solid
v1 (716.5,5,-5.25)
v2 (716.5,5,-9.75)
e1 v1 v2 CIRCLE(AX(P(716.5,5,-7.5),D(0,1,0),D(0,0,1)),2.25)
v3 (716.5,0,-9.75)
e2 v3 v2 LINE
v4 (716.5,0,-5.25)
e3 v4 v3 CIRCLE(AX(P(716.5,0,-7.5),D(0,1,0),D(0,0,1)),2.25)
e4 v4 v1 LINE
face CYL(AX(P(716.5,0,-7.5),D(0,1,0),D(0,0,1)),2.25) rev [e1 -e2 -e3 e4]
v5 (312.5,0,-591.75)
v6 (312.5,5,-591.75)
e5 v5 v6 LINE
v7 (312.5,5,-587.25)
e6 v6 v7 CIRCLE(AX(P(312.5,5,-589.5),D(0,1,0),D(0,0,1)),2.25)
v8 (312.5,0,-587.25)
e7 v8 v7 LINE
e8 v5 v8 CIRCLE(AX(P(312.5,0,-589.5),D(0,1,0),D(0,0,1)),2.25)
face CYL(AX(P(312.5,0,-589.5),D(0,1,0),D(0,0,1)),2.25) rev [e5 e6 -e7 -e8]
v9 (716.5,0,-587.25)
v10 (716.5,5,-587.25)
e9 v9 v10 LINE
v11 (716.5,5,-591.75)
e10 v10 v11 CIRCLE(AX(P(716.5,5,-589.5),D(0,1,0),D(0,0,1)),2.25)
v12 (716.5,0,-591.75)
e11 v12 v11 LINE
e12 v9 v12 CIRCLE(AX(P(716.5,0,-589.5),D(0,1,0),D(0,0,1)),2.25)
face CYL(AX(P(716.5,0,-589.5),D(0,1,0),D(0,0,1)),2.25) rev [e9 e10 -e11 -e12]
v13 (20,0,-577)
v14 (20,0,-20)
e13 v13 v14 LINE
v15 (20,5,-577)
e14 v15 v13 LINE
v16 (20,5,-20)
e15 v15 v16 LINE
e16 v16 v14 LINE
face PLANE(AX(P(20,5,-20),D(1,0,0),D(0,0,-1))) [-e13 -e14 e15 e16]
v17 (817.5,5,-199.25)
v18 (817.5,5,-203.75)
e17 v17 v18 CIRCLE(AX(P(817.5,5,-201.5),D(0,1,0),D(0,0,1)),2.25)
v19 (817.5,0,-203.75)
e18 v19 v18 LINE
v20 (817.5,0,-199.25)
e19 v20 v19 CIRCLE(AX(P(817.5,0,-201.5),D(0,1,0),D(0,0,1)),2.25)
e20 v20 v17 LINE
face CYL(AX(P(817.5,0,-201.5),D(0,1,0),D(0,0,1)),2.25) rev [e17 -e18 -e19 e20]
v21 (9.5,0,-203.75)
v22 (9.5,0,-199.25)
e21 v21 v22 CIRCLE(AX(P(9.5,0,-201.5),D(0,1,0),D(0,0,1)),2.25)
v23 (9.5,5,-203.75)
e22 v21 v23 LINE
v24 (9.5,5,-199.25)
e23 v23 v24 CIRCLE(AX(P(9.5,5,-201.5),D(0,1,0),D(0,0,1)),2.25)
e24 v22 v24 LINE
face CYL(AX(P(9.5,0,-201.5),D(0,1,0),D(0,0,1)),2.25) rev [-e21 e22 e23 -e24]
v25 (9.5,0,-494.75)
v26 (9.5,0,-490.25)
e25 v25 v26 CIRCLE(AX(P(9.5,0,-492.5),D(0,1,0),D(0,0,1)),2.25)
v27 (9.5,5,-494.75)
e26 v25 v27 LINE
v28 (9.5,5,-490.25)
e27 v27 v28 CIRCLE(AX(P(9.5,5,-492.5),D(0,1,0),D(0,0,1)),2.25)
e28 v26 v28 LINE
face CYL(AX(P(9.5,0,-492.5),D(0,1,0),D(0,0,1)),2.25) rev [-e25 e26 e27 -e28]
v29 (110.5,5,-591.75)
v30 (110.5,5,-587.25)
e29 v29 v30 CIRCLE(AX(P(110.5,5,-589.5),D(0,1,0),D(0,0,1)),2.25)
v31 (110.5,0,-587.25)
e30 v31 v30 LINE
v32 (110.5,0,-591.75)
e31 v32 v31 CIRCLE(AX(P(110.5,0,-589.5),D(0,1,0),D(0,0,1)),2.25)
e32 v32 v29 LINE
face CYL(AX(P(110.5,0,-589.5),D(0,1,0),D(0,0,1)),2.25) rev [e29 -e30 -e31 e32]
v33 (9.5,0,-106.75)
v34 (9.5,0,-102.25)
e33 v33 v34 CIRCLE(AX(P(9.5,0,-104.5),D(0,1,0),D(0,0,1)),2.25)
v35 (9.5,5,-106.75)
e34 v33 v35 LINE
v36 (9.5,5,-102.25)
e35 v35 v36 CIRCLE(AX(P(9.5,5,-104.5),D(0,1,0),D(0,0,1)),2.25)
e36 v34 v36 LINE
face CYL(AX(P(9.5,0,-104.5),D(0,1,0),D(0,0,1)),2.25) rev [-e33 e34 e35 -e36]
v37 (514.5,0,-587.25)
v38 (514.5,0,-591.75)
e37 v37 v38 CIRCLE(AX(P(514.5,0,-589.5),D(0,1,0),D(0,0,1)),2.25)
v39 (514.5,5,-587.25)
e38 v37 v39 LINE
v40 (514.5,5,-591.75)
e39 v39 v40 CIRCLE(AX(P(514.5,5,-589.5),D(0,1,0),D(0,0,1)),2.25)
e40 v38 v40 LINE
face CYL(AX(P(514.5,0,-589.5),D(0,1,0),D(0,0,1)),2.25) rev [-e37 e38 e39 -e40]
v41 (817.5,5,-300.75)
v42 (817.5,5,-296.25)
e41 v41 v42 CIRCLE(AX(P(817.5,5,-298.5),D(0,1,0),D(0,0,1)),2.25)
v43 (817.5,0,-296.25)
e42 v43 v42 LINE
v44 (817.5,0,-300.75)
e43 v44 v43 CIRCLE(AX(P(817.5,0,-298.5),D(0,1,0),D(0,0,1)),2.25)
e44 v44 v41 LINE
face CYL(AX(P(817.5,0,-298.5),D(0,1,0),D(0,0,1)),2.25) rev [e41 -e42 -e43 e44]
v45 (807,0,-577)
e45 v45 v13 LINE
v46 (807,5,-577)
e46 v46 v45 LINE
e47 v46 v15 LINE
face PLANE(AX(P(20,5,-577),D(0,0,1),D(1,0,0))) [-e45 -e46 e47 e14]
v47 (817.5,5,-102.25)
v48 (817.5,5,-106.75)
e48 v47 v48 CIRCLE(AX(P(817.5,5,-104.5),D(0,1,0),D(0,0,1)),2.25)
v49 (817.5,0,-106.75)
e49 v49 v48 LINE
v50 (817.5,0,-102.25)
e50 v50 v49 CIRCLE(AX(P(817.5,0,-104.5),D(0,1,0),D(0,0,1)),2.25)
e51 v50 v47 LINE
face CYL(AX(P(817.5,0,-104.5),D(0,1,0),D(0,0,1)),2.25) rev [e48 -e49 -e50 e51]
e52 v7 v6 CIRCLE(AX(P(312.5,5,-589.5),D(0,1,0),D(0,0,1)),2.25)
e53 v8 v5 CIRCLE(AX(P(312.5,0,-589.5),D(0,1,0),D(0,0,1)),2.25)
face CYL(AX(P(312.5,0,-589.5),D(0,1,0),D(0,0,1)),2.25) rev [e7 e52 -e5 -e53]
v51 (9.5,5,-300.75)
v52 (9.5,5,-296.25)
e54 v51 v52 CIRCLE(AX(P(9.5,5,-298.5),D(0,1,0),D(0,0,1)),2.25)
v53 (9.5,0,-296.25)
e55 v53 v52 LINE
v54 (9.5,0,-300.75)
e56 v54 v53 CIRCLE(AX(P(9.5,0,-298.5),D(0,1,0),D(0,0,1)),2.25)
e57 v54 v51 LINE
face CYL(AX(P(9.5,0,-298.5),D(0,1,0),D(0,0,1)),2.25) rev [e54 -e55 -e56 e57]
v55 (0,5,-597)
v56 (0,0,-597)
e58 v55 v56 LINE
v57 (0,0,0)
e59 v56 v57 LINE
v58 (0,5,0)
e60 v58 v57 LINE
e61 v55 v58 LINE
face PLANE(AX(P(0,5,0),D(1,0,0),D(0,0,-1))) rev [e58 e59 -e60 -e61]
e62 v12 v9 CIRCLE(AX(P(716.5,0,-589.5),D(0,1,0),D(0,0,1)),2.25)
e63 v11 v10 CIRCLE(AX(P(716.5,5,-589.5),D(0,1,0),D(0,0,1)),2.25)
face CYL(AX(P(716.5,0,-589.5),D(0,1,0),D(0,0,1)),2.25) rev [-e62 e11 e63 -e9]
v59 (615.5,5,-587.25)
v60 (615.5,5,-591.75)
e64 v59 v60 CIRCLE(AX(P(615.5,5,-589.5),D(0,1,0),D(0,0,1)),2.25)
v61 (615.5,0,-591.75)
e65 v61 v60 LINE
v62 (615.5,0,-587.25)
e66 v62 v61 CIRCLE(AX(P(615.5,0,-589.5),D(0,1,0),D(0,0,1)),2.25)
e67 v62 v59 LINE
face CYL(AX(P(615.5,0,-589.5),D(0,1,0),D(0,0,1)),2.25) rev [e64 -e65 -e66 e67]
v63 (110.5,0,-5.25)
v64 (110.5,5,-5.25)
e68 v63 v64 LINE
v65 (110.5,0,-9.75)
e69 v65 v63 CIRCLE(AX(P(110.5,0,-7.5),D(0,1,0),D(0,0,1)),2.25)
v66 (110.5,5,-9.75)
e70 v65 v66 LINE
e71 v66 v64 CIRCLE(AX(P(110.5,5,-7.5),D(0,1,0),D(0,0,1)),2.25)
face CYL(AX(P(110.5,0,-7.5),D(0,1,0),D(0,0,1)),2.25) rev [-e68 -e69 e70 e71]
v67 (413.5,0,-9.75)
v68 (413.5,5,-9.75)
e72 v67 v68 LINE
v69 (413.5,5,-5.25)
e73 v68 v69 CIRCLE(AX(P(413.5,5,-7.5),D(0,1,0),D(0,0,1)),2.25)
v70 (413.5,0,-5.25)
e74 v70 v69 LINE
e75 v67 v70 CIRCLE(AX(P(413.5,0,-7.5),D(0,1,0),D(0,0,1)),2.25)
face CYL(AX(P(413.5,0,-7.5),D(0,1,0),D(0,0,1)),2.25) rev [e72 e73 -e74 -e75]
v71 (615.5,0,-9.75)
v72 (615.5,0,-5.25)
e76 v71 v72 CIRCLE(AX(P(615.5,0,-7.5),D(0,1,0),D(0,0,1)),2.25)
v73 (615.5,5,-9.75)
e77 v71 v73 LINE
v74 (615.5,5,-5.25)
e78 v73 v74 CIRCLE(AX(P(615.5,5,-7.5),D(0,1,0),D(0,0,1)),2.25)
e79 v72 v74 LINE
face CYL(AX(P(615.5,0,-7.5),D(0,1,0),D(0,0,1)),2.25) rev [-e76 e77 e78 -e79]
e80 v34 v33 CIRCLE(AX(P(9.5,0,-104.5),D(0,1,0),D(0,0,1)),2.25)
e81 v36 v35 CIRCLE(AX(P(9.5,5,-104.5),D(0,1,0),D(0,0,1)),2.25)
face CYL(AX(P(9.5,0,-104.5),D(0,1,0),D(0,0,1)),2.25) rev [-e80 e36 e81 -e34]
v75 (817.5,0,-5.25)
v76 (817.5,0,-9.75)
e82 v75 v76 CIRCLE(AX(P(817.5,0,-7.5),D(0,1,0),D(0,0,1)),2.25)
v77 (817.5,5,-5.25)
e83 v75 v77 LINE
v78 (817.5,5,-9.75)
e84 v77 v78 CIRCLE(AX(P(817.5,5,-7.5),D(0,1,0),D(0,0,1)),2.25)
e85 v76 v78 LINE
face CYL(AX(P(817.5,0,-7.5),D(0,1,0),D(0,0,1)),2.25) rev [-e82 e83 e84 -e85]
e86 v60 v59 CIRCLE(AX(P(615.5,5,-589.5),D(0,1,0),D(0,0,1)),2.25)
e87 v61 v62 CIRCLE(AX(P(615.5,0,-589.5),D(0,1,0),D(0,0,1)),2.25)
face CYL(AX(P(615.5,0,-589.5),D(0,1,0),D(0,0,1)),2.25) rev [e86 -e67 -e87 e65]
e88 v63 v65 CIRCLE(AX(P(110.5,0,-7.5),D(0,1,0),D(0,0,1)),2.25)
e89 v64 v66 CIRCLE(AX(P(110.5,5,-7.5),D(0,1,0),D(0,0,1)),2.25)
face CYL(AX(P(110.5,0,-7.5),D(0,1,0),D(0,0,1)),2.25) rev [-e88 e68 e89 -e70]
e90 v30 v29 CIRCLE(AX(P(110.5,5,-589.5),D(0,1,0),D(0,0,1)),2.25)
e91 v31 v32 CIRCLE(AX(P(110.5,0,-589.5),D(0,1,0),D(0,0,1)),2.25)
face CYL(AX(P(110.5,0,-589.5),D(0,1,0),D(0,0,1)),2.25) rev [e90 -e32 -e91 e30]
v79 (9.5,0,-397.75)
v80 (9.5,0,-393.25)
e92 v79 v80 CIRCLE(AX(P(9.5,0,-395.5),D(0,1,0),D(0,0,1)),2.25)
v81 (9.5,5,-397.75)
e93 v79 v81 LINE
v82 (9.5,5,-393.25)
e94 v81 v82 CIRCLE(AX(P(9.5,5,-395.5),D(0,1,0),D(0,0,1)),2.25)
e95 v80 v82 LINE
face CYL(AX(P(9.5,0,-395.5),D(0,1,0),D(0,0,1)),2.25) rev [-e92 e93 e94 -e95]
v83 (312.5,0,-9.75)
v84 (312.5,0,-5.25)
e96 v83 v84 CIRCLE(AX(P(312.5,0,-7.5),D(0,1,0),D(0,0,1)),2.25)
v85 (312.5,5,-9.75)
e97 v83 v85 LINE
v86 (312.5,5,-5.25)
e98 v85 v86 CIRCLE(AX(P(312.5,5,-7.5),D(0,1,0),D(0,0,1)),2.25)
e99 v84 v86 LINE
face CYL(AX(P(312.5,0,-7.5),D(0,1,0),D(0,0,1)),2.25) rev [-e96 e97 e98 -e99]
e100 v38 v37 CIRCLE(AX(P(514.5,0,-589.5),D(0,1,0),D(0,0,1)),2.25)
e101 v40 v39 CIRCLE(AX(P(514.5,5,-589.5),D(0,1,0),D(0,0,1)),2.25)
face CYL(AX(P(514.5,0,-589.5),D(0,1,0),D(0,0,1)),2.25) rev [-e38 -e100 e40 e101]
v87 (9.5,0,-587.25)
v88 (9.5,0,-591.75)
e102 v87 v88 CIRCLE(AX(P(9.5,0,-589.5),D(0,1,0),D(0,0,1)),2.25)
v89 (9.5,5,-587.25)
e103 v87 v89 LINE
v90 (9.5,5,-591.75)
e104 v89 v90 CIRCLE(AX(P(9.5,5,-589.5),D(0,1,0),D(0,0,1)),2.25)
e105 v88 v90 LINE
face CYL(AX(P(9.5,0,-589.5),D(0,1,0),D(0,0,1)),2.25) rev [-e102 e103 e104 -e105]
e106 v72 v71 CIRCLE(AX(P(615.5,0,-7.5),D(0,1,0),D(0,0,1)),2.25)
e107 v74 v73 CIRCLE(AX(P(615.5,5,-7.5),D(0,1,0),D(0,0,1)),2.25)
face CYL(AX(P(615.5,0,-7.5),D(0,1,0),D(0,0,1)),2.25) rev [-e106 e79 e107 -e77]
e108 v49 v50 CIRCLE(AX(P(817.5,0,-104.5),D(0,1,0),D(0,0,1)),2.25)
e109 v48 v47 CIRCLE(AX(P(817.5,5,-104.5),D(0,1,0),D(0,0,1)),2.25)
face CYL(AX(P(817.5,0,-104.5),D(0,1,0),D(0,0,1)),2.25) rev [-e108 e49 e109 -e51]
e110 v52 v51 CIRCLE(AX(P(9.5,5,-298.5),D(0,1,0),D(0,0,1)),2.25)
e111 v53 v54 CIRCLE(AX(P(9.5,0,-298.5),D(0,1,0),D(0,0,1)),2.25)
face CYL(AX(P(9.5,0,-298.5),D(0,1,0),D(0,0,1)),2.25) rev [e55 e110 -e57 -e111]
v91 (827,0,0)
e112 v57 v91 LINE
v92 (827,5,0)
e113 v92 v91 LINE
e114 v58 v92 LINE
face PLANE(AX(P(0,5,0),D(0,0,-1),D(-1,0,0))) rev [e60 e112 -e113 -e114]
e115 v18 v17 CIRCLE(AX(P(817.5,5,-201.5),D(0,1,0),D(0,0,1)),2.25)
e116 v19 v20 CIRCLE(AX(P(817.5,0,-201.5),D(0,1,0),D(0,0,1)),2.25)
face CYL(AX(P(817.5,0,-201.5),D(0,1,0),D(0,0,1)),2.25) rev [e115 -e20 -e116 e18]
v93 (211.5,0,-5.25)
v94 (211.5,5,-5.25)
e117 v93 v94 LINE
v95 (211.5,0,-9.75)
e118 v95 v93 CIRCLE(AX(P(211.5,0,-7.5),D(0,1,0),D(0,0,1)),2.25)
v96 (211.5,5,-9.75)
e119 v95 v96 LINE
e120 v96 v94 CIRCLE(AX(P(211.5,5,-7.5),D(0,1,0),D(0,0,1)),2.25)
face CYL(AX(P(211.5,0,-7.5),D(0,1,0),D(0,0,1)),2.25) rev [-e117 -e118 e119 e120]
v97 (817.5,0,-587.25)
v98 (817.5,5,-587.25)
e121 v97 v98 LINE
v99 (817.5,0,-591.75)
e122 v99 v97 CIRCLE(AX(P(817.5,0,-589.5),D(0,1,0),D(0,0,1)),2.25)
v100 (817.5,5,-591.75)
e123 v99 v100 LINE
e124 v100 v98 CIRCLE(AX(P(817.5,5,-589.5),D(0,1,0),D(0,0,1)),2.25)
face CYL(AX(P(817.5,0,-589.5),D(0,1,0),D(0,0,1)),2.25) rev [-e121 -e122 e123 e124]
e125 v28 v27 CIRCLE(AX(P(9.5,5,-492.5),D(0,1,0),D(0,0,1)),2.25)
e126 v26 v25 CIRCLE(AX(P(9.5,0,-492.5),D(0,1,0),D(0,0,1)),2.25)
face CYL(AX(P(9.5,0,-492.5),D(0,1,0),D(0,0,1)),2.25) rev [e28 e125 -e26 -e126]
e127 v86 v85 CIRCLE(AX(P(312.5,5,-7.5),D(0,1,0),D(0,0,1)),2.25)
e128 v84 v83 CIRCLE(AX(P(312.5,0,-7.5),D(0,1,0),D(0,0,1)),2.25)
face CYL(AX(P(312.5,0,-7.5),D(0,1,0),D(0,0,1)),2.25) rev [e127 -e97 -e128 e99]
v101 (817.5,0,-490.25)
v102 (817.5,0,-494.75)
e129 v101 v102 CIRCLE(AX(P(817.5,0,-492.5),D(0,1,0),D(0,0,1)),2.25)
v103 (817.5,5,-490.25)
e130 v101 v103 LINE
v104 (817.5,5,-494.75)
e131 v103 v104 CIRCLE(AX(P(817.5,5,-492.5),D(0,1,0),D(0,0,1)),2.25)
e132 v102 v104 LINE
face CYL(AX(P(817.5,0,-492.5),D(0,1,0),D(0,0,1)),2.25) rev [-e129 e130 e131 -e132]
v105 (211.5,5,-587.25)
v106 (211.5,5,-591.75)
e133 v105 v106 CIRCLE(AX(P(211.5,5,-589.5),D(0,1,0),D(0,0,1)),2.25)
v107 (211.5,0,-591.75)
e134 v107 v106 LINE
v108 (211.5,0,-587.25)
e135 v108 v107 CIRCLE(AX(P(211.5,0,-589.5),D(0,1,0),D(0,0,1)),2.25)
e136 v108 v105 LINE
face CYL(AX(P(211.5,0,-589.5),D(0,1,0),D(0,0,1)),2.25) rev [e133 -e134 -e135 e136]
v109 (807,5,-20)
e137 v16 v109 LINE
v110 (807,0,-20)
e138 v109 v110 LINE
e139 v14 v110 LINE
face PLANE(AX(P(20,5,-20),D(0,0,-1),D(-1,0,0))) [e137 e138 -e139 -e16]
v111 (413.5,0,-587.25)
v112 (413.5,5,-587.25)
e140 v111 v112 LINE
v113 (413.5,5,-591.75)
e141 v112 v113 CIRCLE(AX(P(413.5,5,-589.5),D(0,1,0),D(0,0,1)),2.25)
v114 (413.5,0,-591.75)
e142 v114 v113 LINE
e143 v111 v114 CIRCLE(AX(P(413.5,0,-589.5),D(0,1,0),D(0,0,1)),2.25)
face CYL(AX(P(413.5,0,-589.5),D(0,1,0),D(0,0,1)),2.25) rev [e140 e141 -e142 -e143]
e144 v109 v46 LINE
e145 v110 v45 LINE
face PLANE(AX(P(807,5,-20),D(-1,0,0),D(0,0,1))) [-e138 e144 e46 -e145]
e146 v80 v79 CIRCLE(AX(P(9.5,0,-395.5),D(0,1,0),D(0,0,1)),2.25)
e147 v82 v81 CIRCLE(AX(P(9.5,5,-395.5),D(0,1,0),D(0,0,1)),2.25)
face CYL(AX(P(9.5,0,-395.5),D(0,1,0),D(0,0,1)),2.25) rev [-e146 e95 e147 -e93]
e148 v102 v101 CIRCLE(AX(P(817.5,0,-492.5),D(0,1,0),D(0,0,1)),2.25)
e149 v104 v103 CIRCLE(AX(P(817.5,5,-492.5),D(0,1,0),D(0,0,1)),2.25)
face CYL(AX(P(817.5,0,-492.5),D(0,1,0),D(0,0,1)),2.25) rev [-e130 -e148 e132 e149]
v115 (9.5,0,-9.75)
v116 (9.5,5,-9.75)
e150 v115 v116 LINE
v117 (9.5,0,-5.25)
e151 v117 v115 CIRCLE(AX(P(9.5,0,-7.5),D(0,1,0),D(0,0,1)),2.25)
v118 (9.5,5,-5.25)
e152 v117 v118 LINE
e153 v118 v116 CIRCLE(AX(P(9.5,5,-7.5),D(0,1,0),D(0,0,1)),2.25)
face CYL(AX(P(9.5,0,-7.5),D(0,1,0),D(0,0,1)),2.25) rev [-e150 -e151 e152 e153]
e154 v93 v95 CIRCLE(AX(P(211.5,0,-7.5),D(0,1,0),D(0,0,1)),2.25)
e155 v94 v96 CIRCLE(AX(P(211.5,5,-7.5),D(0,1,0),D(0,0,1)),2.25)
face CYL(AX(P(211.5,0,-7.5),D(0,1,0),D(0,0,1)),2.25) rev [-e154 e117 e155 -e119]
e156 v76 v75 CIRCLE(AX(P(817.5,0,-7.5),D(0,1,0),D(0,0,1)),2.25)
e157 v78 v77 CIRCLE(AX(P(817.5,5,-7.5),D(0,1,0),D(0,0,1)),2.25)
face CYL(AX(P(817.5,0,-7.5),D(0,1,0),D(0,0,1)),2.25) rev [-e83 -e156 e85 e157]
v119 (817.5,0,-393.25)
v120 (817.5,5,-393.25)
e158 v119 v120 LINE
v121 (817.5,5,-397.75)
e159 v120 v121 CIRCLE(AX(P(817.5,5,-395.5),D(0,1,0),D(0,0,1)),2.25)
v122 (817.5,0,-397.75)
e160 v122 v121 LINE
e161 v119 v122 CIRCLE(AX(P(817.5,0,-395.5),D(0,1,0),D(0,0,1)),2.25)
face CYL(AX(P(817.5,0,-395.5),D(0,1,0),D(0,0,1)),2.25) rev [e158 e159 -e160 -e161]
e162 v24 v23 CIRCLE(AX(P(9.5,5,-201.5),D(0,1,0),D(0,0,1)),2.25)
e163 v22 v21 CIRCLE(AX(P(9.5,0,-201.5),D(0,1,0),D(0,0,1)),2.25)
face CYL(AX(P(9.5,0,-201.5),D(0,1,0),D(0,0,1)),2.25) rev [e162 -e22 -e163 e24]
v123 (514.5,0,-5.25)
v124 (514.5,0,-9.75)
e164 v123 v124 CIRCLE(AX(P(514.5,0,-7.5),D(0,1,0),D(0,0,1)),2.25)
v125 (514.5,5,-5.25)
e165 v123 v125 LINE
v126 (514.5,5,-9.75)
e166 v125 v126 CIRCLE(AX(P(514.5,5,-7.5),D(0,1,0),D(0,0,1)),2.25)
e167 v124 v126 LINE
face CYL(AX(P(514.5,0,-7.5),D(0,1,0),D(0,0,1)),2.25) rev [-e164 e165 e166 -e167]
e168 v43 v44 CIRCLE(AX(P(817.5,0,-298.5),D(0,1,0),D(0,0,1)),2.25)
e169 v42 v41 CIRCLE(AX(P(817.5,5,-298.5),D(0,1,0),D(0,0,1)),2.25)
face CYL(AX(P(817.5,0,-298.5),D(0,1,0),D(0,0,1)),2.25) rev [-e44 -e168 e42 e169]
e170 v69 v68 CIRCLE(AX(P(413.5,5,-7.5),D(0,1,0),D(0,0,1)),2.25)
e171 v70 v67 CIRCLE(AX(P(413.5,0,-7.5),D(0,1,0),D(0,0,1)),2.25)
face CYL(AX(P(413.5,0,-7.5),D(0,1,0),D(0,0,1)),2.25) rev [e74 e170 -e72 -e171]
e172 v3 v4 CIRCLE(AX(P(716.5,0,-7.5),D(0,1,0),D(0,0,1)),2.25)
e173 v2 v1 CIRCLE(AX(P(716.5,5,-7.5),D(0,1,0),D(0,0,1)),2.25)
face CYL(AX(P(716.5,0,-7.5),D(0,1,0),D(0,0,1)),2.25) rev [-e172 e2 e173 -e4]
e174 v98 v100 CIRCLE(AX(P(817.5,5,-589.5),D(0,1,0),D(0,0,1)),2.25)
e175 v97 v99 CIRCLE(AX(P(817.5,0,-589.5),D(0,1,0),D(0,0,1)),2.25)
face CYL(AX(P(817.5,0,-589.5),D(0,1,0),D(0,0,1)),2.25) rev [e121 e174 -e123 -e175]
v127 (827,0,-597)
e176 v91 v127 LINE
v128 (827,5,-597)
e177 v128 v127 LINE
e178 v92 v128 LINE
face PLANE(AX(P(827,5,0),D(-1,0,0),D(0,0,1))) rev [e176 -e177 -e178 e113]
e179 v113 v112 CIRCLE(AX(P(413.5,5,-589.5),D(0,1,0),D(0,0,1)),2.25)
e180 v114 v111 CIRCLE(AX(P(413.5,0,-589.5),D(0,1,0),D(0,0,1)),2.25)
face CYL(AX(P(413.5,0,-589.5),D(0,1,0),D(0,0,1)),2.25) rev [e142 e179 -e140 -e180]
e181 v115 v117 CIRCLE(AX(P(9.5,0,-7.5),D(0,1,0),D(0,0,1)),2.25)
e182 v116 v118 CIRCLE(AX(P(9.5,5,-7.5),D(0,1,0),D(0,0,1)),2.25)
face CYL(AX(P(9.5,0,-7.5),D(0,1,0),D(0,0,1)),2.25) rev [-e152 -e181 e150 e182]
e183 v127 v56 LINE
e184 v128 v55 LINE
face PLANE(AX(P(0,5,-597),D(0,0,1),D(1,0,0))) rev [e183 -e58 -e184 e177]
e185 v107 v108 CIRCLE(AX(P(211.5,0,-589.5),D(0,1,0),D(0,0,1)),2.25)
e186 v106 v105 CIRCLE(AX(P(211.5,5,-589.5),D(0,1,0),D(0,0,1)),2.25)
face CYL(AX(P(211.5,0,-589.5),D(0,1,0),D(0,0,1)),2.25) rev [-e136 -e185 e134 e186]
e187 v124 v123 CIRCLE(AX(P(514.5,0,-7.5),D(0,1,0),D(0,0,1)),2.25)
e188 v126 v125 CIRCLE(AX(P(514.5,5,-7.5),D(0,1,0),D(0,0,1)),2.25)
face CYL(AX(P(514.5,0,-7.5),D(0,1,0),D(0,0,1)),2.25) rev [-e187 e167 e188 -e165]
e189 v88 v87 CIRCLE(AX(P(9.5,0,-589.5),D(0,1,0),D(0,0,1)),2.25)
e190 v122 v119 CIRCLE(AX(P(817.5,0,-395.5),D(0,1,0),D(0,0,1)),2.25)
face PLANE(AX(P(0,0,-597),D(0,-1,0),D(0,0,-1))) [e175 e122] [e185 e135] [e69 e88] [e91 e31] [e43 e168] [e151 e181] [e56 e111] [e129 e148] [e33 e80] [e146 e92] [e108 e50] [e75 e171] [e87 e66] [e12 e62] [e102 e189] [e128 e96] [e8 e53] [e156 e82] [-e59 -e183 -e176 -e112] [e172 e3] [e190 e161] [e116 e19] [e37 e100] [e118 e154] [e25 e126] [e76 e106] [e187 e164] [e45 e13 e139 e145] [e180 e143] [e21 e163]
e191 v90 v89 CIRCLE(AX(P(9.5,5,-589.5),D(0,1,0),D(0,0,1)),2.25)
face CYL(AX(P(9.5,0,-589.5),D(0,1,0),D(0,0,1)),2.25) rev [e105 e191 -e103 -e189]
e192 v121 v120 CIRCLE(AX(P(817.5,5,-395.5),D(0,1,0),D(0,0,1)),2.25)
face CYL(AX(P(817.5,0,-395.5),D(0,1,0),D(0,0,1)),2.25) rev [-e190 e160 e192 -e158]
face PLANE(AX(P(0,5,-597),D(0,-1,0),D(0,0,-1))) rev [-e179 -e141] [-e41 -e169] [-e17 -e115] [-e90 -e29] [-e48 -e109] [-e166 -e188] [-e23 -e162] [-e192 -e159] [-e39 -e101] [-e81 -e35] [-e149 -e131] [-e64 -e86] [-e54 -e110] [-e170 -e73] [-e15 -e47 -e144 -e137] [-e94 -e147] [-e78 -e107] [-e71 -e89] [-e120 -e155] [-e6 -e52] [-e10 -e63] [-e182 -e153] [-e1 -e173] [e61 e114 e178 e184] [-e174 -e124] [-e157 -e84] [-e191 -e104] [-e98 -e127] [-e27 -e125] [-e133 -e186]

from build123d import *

# Parameters (mm, degrees)
SKETCH_1_W                        = 827
SKETCH_1_H                        = 597
SKETCH_1_W_2                      = 787
SKETCH_1_H_2                      = 557
EXTRUDE_1_DEPTH                   = 5
SKETCH_2_R                        = 2.25
CUT_EXTRUDE_1_DEPTH               = 5
PATTERN_LINEAR_1_COUNT            = 9
PATTERN_LINEAR_1_PITCH            = 101
PATTERN_LINEAR_2_COUNT            = 7
PATTERN_LINEAR_2_PITCH            = 97
PATTERN_LINEAR_3_COPY_1_SKETCH_R  = 2.25
PATTERN_LINEAR_3_COPY_1_DEPTH     = 5
PATTERN_LINEAR_3_COPY_2_SKETCH_R  = 2.25
PATTERN_LINEAR_3_COPY_2_DEPTH     = 5
PATTERN_LINEAR_3_COPY_3_SKETCH_R  = 2.25
PATTERN_LINEAR_3_COPY_3_DEPTH     = 5
PATTERN_LINEAR_3_COPY_4_SKETCH_R  = 2.25
PATTERN_LINEAR_3_COPY_4_DEPTH     = 5
PATTERN_LINEAR_3_COPY_5_SKETCH_R  = 2.25
PATTERN_LINEAR_3_COPY_5_DEPTH     = 5
PATTERN_LINEAR_3_COPY_6_SKETCH_R  = 2.25
PATTERN_LINEAR_3_COPY_6_DEPTH     = 5
PATTERN_LINEAR_3_COPY_7_SKETCH_R  = 2.25
PATTERN_LINEAR_3_COPY_7_DEPTH     = 5
PATTERN_LINEAR_3_COPY_8_SKETCH_R  = 2.25
PATTERN_LINEAR_3_COPY_8_DEPTH     = 5
PATTERN_LINEAR_3_COPY_9_SKETCH_R  = 2.25
PATTERN_LINEAR_3_COPY_9_DEPTH     = 5
PATTERN_LINEAR_3_COPY_10_SKETCH_R = 2.25
PATTERN_LINEAR_3_COPY_10_DEPTH    = 5
PATTERN_LINEAR_3_COPY_11_SKETCH_R = 2.25
PATTERN_LINEAR_3_COPY_11_DEPTH    = 5
PATTERN_LINEAR_3_COPY_12_SKETCH_R = 2.25
PATTERN_LINEAR_3_COPY_12_DEPTH    = 5
PATTERN_LINEAR_3_COPY_13_SKETCH_R = 2.25
PATTERN_LINEAR_3_COPY_13_DEPTH    = 5
PATTERN_LINEAR_3_COPY_14_SKETCH_R = 2.25
PATTERN_LINEAR_3_COPY_14_DEPTH    = 5
PATTERN_LINEAR_3_COPY_15_SKETCH_R = 2.25
PATTERN_LINEAR_3_COPY_15_DEPTH    = 5
PATTERN_LINEAR_3_COPY_16_SKETCH_R = 2.25
PATTERN_LINEAR_3_COPY_16_DEPTH    = 5
PATTERN_LINEAR_3_COPY_17_SKETCH_R = 2.25
PATTERN_LINEAR_3_COPY_17_DEPTH    = 5
PATTERN_LINEAR_3_COPY_18_SKETCH_R = 2.25
PATTERN_LINEAR_3_COPY_18_DEPTH    = 5
PATTERN_LINEAR_3_COPY_19_SKETCH_R = 2.25
PATTERN_LINEAR_3_COPY_19_DEPTH    = 5
PATTERN_LINEAR_3_COPY_20_SKETCH_R = 2.25
PATTERN_LINEAR_3_COPY_20_DEPTH    = 5
PATTERN_LINEAR_3_COPY_21_SKETCH_R = 2.25
PATTERN_LINEAR_3_COPY_21_DEPTH    = 5
PATTERN_LINEAR_3_COPY_22_SKETCH_R = 2.25
PATTERN_LINEAR_3_COPY_22_DEPTH    = 5
PATTERN_LINEAR_3_COPY_23_SKETCH_R = 2.25
PATTERN_LINEAR_3_COPY_23_DEPTH    = 5
PATTERN_LINEAR_3_COPY_24_SKETCH_R = 2.25
PATTERN_LINEAR_3_COPY_24_DEPTH    = 5
PATTERN_LINEAR_3_COPY_25_SKETCH_R = 2.25
PATTERN_LINEAR_3_COPY_25_DEPTH    = 5
PATTERN_LINEAR_3_COPY_26_SKETCH_R = 2.25
PATTERN_LINEAR_3_COPY_26_DEPTH    = 5
PATTERN_LINEAR_3_COPY_27_SKETCH_R = 2.25
PATTERN_LINEAR_3_COPY_27_DEPTH    = 5
PATTERN_LINEAR_3_COPY_28_SKETCH_R = 2.25
PATTERN_LINEAR_3_COPY_28_DEPTH    = 5
PATTERN_LINEAR_3_COPY_29_SKETCH_R = 2.25
PATTERN_LINEAR_3_COPY_29_DEPTH    = 5
PATTERN_LINEAR_3_COPY_30_SKETCH_R = 2.25
PATTERN_LINEAR_3_COPY_30_DEPTH    = 5
PATTERN_LINEAR_3_COPY_31_SKETCH_R = 2.25
PATTERN_LINEAR_3_COPY_31_DEPTH    = 5
PATTERN_LINEAR_3_COPY_32_SKETCH_R = 2.25
PATTERN_LINEAR_3_COPY_32_DEPTH    = 5
PATTERN_LINEAR_3_COPY_33_SKETCH_R = 2.25
PATTERN_LINEAR_3_COPY_33_DEPTH    = 5
PATTERN_LINEAR_3_COPY_34_SKETCH_R = 2.25
PATTERN_LINEAR_3_COPY_34_DEPTH    = 5
PATTERN_LINEAR_3_COPY_35_SKETCH_R = 2.25
PATTERN_LINEAR_3_COPY_35_DEPTH    = 5
PATTERN_LINEAR_3_COPY_36_SKETCH_R = 2.25
PATTERN_LINEAR_3_COPY_36_DEPTH    = 5
PATTERN_LINEAR_3_COPY_37_SKETCH_R = 2.25
PATTERN_LINEAR_3_COPY_37_DEPTH    = 5
PATTERN_LINEAR_3_COPY_38_SKETCH_R = 2.25
PATTERN_LINEAR_3_COPY_38_DEPTH    = 5
PATTERN_LINEAR_3_COPY_39_SKETCH_R = 2.25
PATTERN_LINEAR_3_COPY_39_DEPTH    = 5
PATTERN_LINEAR_3_COPY_40_SKETCH_R = 2.25
PATTERN_LINEAR_3_COPY_40_DEPTH    = 5
PATTERN_LINEAR_3_COPY_41_SKETCH_R = 2.25
PATTERN_LINEAR_3_COPY_41_DEPTH    = 5
PATTERN_LINEAR_3_COPY_42_SKETCH_R = 2.25
PATTERN_LINEAR_3_COPY_42_DEPTH    = 5
PATTERN_LINEAR_3_COPY_43_SKETCH_R = 2.25
PATTERN_LINEAR_3_COPY_43_DEPTH    = 5
PATTERN_LINEAR_3_COPY_44_SKETCH_R = 2.25
PATTERN_LINEAR_3_COPY_44_DEPTH    = 5
PATTERN_LINEAR_3_COPY_45_SKETCH_R = 2.25
PATTERN_LINEAR_3_COPY_45_DEPTH    = 5
PATTERN_LINEAR_3_COPY_46_SKETCH_R = 2.25
PATTERN_LINEAR_3_COPY_46_DEPTH    = 5
PATTERN_LINEAR_3_COPY_47_SKETCH_R = 2.25
PATTERN_LINEAR_3_COPY_47_DEPTH    = 5
PATTERN_LINEAR_3_COPY_48_SKETCH_R = 2.25
PATTERN_LINEAR_3_COPY_48_DEPTH    = 5
PATTERN_LINEAR_3_COPY_49_SKETCH_R = 2.25
PATTERN_LINEAR_3_COPY_49_DEPTH    = 5
PATTERN_LINEAR_3_COPY_50_SKETCH_R = 2.25
PATTERN_LINEAR_3_COPY_50_DEPTH    = 5
PATTERN_LINEAR_3_COPY_51_SKETCH_R = 2.25
PATTERN_LINEAR_3_COPY_51_DEPTH    = 5
PATTERN_LINEAR_3_COPY_52_SKETCH_R = 2.25
PATTERN_LINEAR_3_COPY_52_DEPTH    = 5
PATTERN_LINEAR_3_COPY_53_SKETCH_R = 2.25
PATTERN_LINEAR_3_COPY_53_DEPTH    = 5
PATTERN_LINEAR_3_COPY_54_SKETCH_R = 2.25
PATTERN_LINEAR_3_COPY_54_DEPTH    = 5
PATTERN_LINEAR_3_COPY_55_SKETCH_R = 2.25
PATTERN_LINEAR_3_COPY_55_DEPTH    = 5
PATTERN_LINEAR_3_COPY_56_SKETCH_R = 2.25
PATTERN_LINEAR_3_COPY_56_DEPTH    = 5


with BuildPart() as part:
    # 草图1 → 拉伸1 (new body)
    with BuildSketch(Plane(origin=(0, 0, 0), x_dir=(1, 0, 0), z_dir=(0, 1, 0))):
        with Locations((413.5, 298.5)):
            Rectangle(SKETCH_1_W, SKETCH_1_H)
        with Locations((413.5, 298.5)):
            Rectangle(SKETCH_1_W_2, SKETCH_1_H_2, mode=Mode.SUBTRACT)
    extrude(amount=EXTRUDE_1_DEPTH)

    # 草图2 → 切除-拉伸1 (cut)
    with BuildSketch(Plane(origin=(0, 5, 0), x_dir=(-1, 0, 0), z_dir=(0, 1, 0))):
        with Locations(Location((-817.5, -589.5, 0), (0, 0, 90))):
            Circle(SKETCH_2_R)
    cut_extrude_1 = extrude(amount=-CUT_EXTRUDE_1_DEPTH, mode=Mode.SUBTRACT)

    # 阵列(线性)1: 切除-拉伸1 ×9
    with Locations(*[(-i * PATTERN_LINEAR_1_PITCH, 0, 0) for i in range(1, PATTERN_LINEAR_1_COUNT)]):
        add(cut_extrude_1, mode=Mode.SUBTRACT)

    # 阵列(线性)2: 切除-拉伸1 ×7
    with Locations(*[(0, 0, i * PATTERN_LINEAR_2_PITCH) for i in range(1, PATTERN_LINEAR_2_COUNT)]):
        add(cut_extrude_1, mode=Mode.SUBTRACT)

    # 阵列(线性)3 copy 1 sketch → 阵列(线性)3 copy 1 (cut)
    with BuildSketch(Plane(origin=(-101, 5, 97), x_dir=(-1, 0, 0), z_dir=(0, 1, 0))):
        with Locations(Location((-817.5, -589.5, 0), (0, 0, 90))):
            Circle(PATTERN_LINEAR_3_COPY_1_SKETCH_R)
    extrude(amount=-PATTERN_LINEAR_3_COPY_1_DEPTH, mode=Mode.SUBTRACT)

    # 阵列(线性)3 copy 2 sketch → 阵列(线性)3 copy 2 (cut)
    with BuildSketch(Plane(origin=(-202, 5, 97), x_dir=(-1, 0, 0), z_dir=(0, 1, 0))):
        with Locations(Location((-817.5, -589.5, 0), (0, 0, 90))):
            Circle(PATTERN_LINEAR_3_COPY_2_SKETCH_R)
    extrude(amount=-PATTERN_LINEAR_3_COPY_2_DEPTH, mode=Mode.SUBTRACT)

    # 阵列(线性)3 copy 3 sketch → 阵列(线性)3 copy 3 (cut)
    with BuildSketch(Plane(origin=(-303, 5, 97), x_dir=(-1, 0, 0), z_dir=(0, 1, 0))):
        with Locations(Location((-817.5, -589.5, 0), (0, 0, 90))):
            Circle(PATTERN_LINEAR_3_COPY_3_SKETCH_R)
    extrude(amount=-PATTERN_LINEAR_3_COPY_3_DEPTH, mode=Mode.SUBTRACT)

    # 阵列(线性)3 copy 4 sketch → 阵列(线性)3 copy 4 (cut)
    with BuildSketch(Plane(origin=(-404, 5, 97), x_dir=(-1, 0, 0), z_dir=(0, 1, 0))):
        with Locations(Location((-817.5, -589.5, 0), (0, 0, 90))):
            Circle(PATTERN_LINEAR_3_COPY_4_SKETCH_R)
    extrude(amount=-PATTERN_LINEAR_3_COPY_4_DEPTH, mode=Mode.SUBTRACT)

    # 阵列(线性)3 copy 5 sketch → 阵列(线性)3 copy 5 (cut)
    with BuildSketch(Plane(origin=(-505, 5, 97), x_dir=(-1, 0, 0), z_dir=(0, 1, 0))):
        with Locations(Location((-817.5, -589.5, 0), (0, 0, 90))):
            Circle(PATTERN_LINEAR_3_COPY_5_SKETCH_R)
    extrude(amount=-PATTERN_LINEAR_3_COPY_5_DEPTH, mode=Mode.SUBTRACT)

    # 阵列(线性)3 copy 6 sketch → 阵列(线性)3 copy 6 (cut)
    with BuildSketch(Plane(origin=(-606, 5, 97), x_dir=(-1, 0, 0), z_dir=(0, 1, 0))):
        with Locations(Location((-817.5, -589.5, 0), (0, 0, 90))):
            Circle(PATTERN_LINEAR_3_COPY_6_SKETCH_R)
    extrude(amount=-PATTERN_LINEAR_3_COPY_6_DEPTH, mode=Mode.SUBTRACT)

    # 阵列(线性)3 copy 7 sketch → 阵列(线性)3 copy 7 (cut)
    with BuildSketch(Plane(origin=(-707, 5, 97), x_dir=(-1, 0, 0), z_dir=(0, 1, 0))):
        with Locations(Location((-817.5, -589.5, 0), (0, 0, 90))):
            Circle(PATTERN_LINEAR_3_COPY_7_SKETCH_R)
    extrude(amount=-PATTERN_LINEAR_3_COPY_7_DEPTH, mode=Mode.SUBTRACT)

    # 阵列(线性)3 copy 8 sketch → 阵列(线性)3 copy 8 (cut)
    with BuildSketch(Plane(origin=(-808, 5, 97), x_dir=(-1, 0, 0), z_dir=(0, 1, 0))):
        with Locations(Location((-817.5, -589.5, 0), (0, 0, 90))):
            Circle(PATTERN_LINEAR_3_COPY_8_SKETCH_R)
    extrude(amount=-PATTERN_LINEAR_3_COPY_8_DEPTH, mode=Mode.SUBTRACT)

    # 阵列(线性)3 copy 9 sketch → 阵列(线性)3 copy 9 (cut)
    with BuildSketch(Plane(origin=(-101, 5, 194), x_dir=(-1, 0, 0), z_dir=(0, 1, 0))):
        with Locations(Location((-817.5, -589.5, 0), (0, 0, 90))):
            Circle(PATTERN_LINEAR_3_COPY_9_SKETCH_R)
    extrude(amount=-PATTERN_LINEAR_3_COPY_9_DEPTH, mode=Mode.SUBTRACT)

    # 阵列(线性)3 copy 10 sketch → 阵列(线性)3 copy 10 (cut)
    with BuildSketch(Plane(origin=(-202, 5, 194), x_dir=(-1, 0, 0), z_dir=(0, 1, 0))):
        with Locations(Location((-817.5, -589.5, 0), (0, 0, 90))):
            Circle(PATTERN_LINEAR_3_COPY_10_SKETCH_R)
    extrude(amount=-PATTERN_LINEAR_3_COPY_10_DEPTH, mode=Mode.SUBTRACT)

    # 阵列(线性)3 copy 11 sketch → 阵列(线性)3 copy 11 (cut)
    with BuildSketch(Plane(origin=(-303, 5, 194), x_dir=(-1, 0, 0), z_dir=(0, 1, 0))):
        with Locations(Location((-817.5, -589.5, 0), (0, 0, 90))):
            Circle(PATTERN_LINEAR_3_COPY_11_SKETCH_R)
    extrude(amount=-PATTERN_LINEAR_3_COPY_11_DEPTH, mode=Mode.SUBTRACT)

    # 阵列(线性)3 copy 12 sketch → 阵列(线性)3 copy 12 (cut)
    with BuildSketch(Plane(origin=(-404, 5, 194), x_dir=(-1, 0, 0), z_dir=(0, 1, 0))):
        with Locations(Location((-817.5, -589.5, 0), (0, 0, 90))):
            Circle(PATTERN_LINEAR_3_COPY_12_SKETCH_R)
    extrude(amount=-PATTERN_LINEAR_3_COPY_12_DEPTH, mode=Mode.SUBTRACT)

    # 阵列(线性)3 copy 13 sketch → 阵列(线性)3 copy 13 (cut)
    with BuildSketch(Plane(origin=(-505, 5, 194), x_dir=(-1, 0, 0), z_dir=(0, 1, 0))):
        with Locations(Location((-817.5, -589.5, 0), (0, 0, 90))):
            Circle(PATTERN_LINEAR_3_COPY_13_SKETCH_R)
    extrude(amount=-PATTERN_LINEAR_3_COPY_13_DEPTH, mode=Mode.SUBTRACT)

    # 阵列(线性)3 copy 14 sketch → 阵列(线性)3 copy 14 (cut)
    with BuildSketch(Plane(origin=(-606, 5, 194), x_dir=(-1, 0, 0), z_dir=(0, 1, 0))):
        with Locations(Location((-817.5, -589.5, 0), (0, 0, 90))):
            Circle(PATTERN_LINEAR_3_COPY_14_SKETCH_R)
    extrude(amount=-PATTERN_LINEAR_3_COPY_14_DEPTH, mode=Mode.SUBTRACT)

    # 阵列(线性)3 copy 15 sketch → 阵列(线性)3 copy 15 (cut)
    with BuildSketch(Plane(origin=(-707, 5, 194), x_dir=(-1, 0, 0), z_dir=(0, 1, 0))):
        with Locations(Location((-817.5, -589.5, 0), (0, 0, 90))):
            Circle(PATTERN_LINEAR_3_COPY_15_SKETCH_R)
    extrude(amount=-PATTERN_LINEAR_3_COPY_15_DEPTH, mode=Mode.SUBTRACT)

    # 阵列(线性)3 copy 16 sketch → 阵列(线性)3 copy 16 (cut)
    with BuildSketch(Plane(origin=(-808, 5, 194), x_dir=(-1, 0, 0), z_dir=(0, 1, 0))):
        with Locations(Location((-817.5, -589.5, 0), (0, 0, 90))):
            Circle(PATTERN_LINEAR_3_COPY_16_SKETCH_R)
    extrude(amount=-PATTERN_LINEAR_3_COPY_16_DEPTH, mode=Mode.SUBTRACT)

    # 阵列(线性)3 copy 17 sketch → 阵列(线性)3 copy 17 (cut)
    with BuildSketch(Plane(origin=(-101, 5, 291), x_dir=(-1, 0, 0), z_dir=(0, 1, 0))):
        with Locations(Location((-817.5, -589.5, 0), (0, 0, 90))):
            Circle(PATTERN_LINEAR_3_COPY_17_SKETCH_R)
    extrude(amount=-PATTERN_LINEAR_3_COPY_17_DEPTH, mode=Mode.SUBTRACT)

    # 阵列(线性)3 copy 18 sketch → 阵列(线性)3 copy 18 (cut)
    with BuildSketch(Plane(origin=(-202, 5, 291), x_dir=(-1, 0, 0), z_dir=(0, 1, 0))):
        with Locations(Location((-817.5, -589.5, 0), (0, 0, 90))):
            Circle(PATTERN_LINEAR_3_COPY_18_SKETCH_R)
    extrude(amount=-PATTERN_LINEAR_3_COPY_18_DEPTH, mode=Mode.SUBTRACT)

    # 阵列(线性)3 copy 19 sketch → 阵列(线性)3 copy 19 (cut)
    with BuildSketch(Plane(origin=(-303, 5, 291), x_dir=(-1, 0, 0), z_dir=(0, 1, 0))):
        with Locations(Location((-817.5, -589.5, 0), (0, 0, 90))):
            Circle(PATTERN_LINEAR_3_COPY_19_SKETCH_R)
    extrude(amount=-PATTERN_LINEAR_3_COPY_19_DEPTH, mode=Mode.SUBTRACT)

    # 阵列(线性)3 copy 20 sketch → 阵列(线性)3 copy 20 (cut)
    with BuildSketch(Plane(origin=(-404, 5, 291), x_dir=(-1, 0, 0), z_dir=(0, 1, 0))):
        with Locations(Location((-817.5, -589.5, 0), (0, 0, 90))):
            Circle(PATTERN_LINEAR_3_COPY_20_SKETCH_R)
    extrude(amount=-PATTERN_LINEAR_3_COPY_20_DEPTH, mode=Mode.SUBTRACT)

    # 阵列(线性)3 copy 21 sketch → 阵列(线性)3 copy 21 (cut)
    with BuildSketch(Plane(origin=(-505, 5, 291), x_dir=(-1, 0, 0), z_dir=(0, 1, 0))):
        with Locations(Location((-817.5, -589.5, 0), (0, 0, 90))):
            Circle(PATTERN_LINEAR_3_COPY_21_SKETCH_R)
    extrude(amount=-PATTERN_LINEAR_3_COPY_21_DEPTH, mode=Mode.SUBTRACT)

    # 阵列(线性)3 copy 22 sketch → 阵列(线性)3 copy 22 (cut)
    with BuildSketch(Plane(origin=(-606, 5, 291), x_dir=(-1, 0, 0), z_dir=(0, 1, 0))):
        with Locations(Location((-817.5, -589.5, 0), (0, 0, 90))):
            Circle(PATTERN_LINEAR_3_COPY_22_SKETCH_R)
    extrude(amount=-PATTERN_LINEAR_3_COPY_22_DEPTH, mode=Mode.SUBTRACT)

    # 阵列(线性)3 copy 23 sketch → 阵列(线性)3 copy 23 (cut)
    with BuildSketch(Plane(origin=(-707, 5, 291), x_dir=(-1, 0, 0), z_dir=(0, 1, 0))):
        with Locations(Location((-817.5, -589.5, 0), (0, 0, 90))):
            Circle(PATTERN_LINEAR_3_COPY_23_SKETCH_R)
    extrude(amount=-PATTERN_LINEAR_3_COPY_23_DEPTH, mode=Mode.SUBTRACT)

    # 阵列(线性)3 copy 24 sketch → 阵列(线性)3 copy 24 (cut)
    with BuildSketch(Plane(origin=(-808, 5, 291), x_dir=(-1, 0, 0), z_dir=(0, 1, 0))):
        with Locations(Location((-817.5, -589.5, 0), (0, 0, 90))):
            Circle(PATTERN_LINEAR_3_COPY_24_SKETCH_R)
    extrude(amount=-PATTERN_LINEAR_3_COPY_24_DEPTH, mode=Mode.SUBTRACT)

    # 阵列(线性)3 copy 25 sketch → 阵列(线性)3 copy 25 (cut)
    with BuildSketch(Plane(origin=(-101, 5, 388), x_dir=(-1, 0, 0), z_dir=(0, 1, 0))):
        with Locations(Location((-817.5, -589.5, 0), (0, 0, 90))):
            Circle(PATTERN_LINEAR_3_COPY_25_SKETCH_R)
    extrude(amount=-PATTERN_LINEAR_3_COPY_25_DEPTH, mode=Mode.SUBTRACT)

    # 阵列(线性)3 copy 26 sketch → 阵列(线性)3 copy 26 (cut)
    with BuildSketch(Plane(origin=(-202, 5, 388), x_dir=(-1, 0, 0), z_dir=(0, 1, 0))):
        with Locations(Location((-817.5, -589.5, 0), (0, 0, 90))):
            Circle(PATTERN_LINEAR_3_COPY_26_SKETCH_R)
    extrude(amount=-PATTERN_LINEAR_3_COPY_26_DEPTH, mode=Mode.SUBTRACT)

    # 阵列(线性)3 copy 27 sketch → 阵列(线性)3 copy 27 (cut)
    with BuildSketch(Plane(origin=(-303, 5, 388), x_dir=(-1, 0, 0), z_dir=(0, 1, 0))):
        with Locations(Location((-817.5, -589.5, 0), (0, 0, 90))):
            Circle(PATTERN_LINEAR_3_COPY_27_SKETCH_R)
    extrude(amount=-PATTERN_LINEAR_3_COPY_27_DEPTH, mode=Mode.SUBTRACT)

    # 阵列(线性)3 copy 28 sketch → 阵列(线性)3 copy 28 (cut)
    with BuildSketch(Plane(origin=(-404, 5, 388), x_dir=(-1, 0, 0), z_dir=(0, 1, 0))):
        with Locations(Location((-817.5, -589.5, 0), (0, 0, 90))):
            Circle(PATTERN_LINEAR_3_COPY_28_SKETCH_R)
    extrude(amount=-PATTERN_LINEAR_3_COPY_28_DEPTH, mode=Mode.SUBTRACT)

    # 阵列(线性)3 copy 29 sketch → 阵列(线性)3 copy 29 (cut)
    with BuildSketch(Plane(origin=(-505, 5, 388), x_dir=(-1, 0, 0), z_dir=(0, 1, 0))):
        with Locations(Location((-817.5, -589.5, 0), (0, 0, 90))):
            Circle(PATTERN_LINEAR_3_COPY_29_SKETCH_R)
    extrude(amount=-PATTERN_LINEAR_3_COPY_29_DEPTH, mode=Mode.SUBTRACT)

    # 阵列(线性)3 copy 30 sketch → 阵列(线性)3 copy 30 (cut)
    with BuildSketch(Plane(origin=(-606, 5, 388), x_dir=(-1, 0, 0), z_dir=(0, 1, 0))):
        with Locations(Location((-817.5, -589.5, 0), (0, 0, 90))):
            Circle(PATTERN_LINEAR_3_COPY_30_SKETCH_R)
    extrude(amount=-PATTERN_LINEAR_3_COPY_30_DEPTH, mode=Mode.SUBTRACT)

    # 阵列(线性)3 copy 31 sketch → 阵列(线性)3 copy 31 (cut)
    with BuildSketch(Plane(origin=(-707, 5, 388), x_dir=(-1, 0, 0), z_dir=(0, 1, 0))):
        with Locations(Location((-817.5, -589.5, 0), (0, 0, 90))):
            Circle(PATTERN_LINEAR_3_COPY_31_SKETCH_R)
    extrude(amount=-PATTERN_LINEAR_3_COPY_31_DEPTH, mode=Mode.SUBTRACT)

    # 阵列(线性)3 copy 32 sketch → 阵列(线性)3 copy 32 (cut)
    with BuildSketch(Plane(origin=(-808, 5, 388), x_dir=(-1, 0, 0), z_dir=(0, 1, 0))):
        with Locations(Location((-817.5, -589.5, 0), (0, 0, 90))):
            Circle(PATTERN_LINEAR_3_COPY_32_SKETCH_R)
    extrude(amount=-PATTERN_LINEAR_3_COPY_32_DEPTH, mode=Mode.SUBTRACT)

    # 阵列(线性)3 copy 33 sketch → 阵列(线性)3 copy 33 (cut)
    with BuildSketch(Plane(origin=(-101, 5, 485), x_dir=(-1, 0, 0), z_dir=(0, 1, 0))):
        with Locations(Location((-817.5, -589.5, 0), (0, 0, 90))):
            Circle(PATTERN_LINEAR_3_COPY_33_SKETCH_R)
    extrude(amount=-PATTERN_LINEAR_3_COPY_33_DEPTH, mode=Mode.SUBTRACT)

    # 阵列(线性)3 copy 34 sketch → 阵列(线性)3 copy 34 (cut)
    with BuildSketch(Plane(origin=(-202, 5, 485), x_dir=(-1, 0, 0), z_dir=(0, 1, 0))):
        with Locations(Location((-817.5, -589.5, 0), (0, 0, 90))):
            Circle(PATTERN_LINEAR_3_COPY_34_SKETCH_R)
    extrude(amount=-PATTERN_LINEAR_3_COPY_34_DEPTH, mode=Mode.SUBTRACT)

    # 阵列(线性)3 copy 35 sketch → 阵列(线性)3 copy 35 (cut)
    with BuildSketch(Plane(origin=(-303, 5, 485), x_dir=(-1, 0, 0), z_dir=(0, 1, 0))):
        with Locations(Location((-817.5, -589.5, 0), (0, 0, 90))):
            Circle(PATTERN_LINEAR_3_COPY_35_SKETCH_R)
    extrude(amount=-PATTERN_LINEAR_3_COPY_35_DEPTH, mode=Mode.SUBTRACT)

    # 阵列(线性)3 copy 36 sketch → 阵列(线性)3 copy 36 (cut)
    with BuildSketch(Plane(origin=(-404, 5, 485), x_dir=(-1, 0, 0), z_dir=(0, 1, 0))):
        with Locations(Location((-817.5, -589.5, 0), (0, 0, 90))):
            Circle(PATTERN_LINEAR_3_COPY_36_SKETCH_R)
    extrude(amount=-PATTERN_LINEAR_3_COPY_36_DEPTH, mode=Mode.SUBTRACT)

    # 阵列(线性)3 copy 37 sketch → 阵列(线性)3 copy 37 (cut)
    with BuildSketch(Plane(origin=(-505, 5, 485), x_dir=(-1, 0, 0), z_dir=(0, 1, 0))):
        with Locations(Location((-817.5, -589.5, 0), (0, 0, 90))):
            Circle(PATTERN_LINEAR_3_COPY_37_SKETCH_R)
    extrude(amount=-PATTERN_LINEAR_3_COPY_37_DEPTH, mode=Mode.SUBTRACT)

    # 阵列(线性)3 copy 38 sketch → 阵列(线性)3 copy 38 (cut)
    with BuildSketch(Plane(origin=(-606, 5, 485), x_dir=(-1, 0, 0), z_dir=(0, 1, 0))):
        with Locations(Location((-817.5, -589.5, 0), (0, 0, 90))):
            Circle(PATTERN_LINEAR_3_COPY_38_SKETCH_R)
    extrude(amount=-PATTERN_LINEAR_3_COPY_38_DEPTH, mode=Mode.SUBTRACT)

    # 阵列(线性)3 copy 39 sketch → 阵列(线性)3 copy 39 (cut)
    with BuildSketch(Plane(origin=(-707, 5, 485), x_dir=(-1, 0, 0), z_dir=(0, 1, 0))):
        with Locations(Location((-817.5, -589.5, 0), (0, 0, 90))):
            Circle(PATTERN_LINEAR_3_COPY_39_SKETCH_R)
    extrude(amount=-PATTERN_LINEAR_3_COPY_39_DEPTH, mode=Mode.SUBTRACT)

    # 阵列(线性)3 copy 40 sketch → 阵列(线性)3 copy 40 (cut)
    with BuildSketch(Plane(origin=(-808, 5, 485), x_dir=(-1, 0, 0), z_dir=(0, 1, 0))):
        with Locations(Location((-817.5, -589.5, 0), (0, 0, 90))):
            Circle(PATTERN_LINEAR_3_COPY_40_SKETCH_R)
    extrude(amount=-PATTERN_LINEAR_3_COPY_40_DEPTH, mode=Mode.SUBTRACT)

    # 阵列(线性)3 copy 41 sketch → 阵列(线性)3 copy 41 (cut)
    with BuildSketch(Plane(origin=(-101, 5, 582), x_dir=(-1, 0, 0), z_dir=(0, 1, 0))):
        with Locations(Location((-817.5, -589.5, 0), (0, 0, 90))):
            Circle(PATTERN_LINEAR_3_COPY_41_SKETCH_R)
    extrude(amount=-PATTERN_LINEAR_3_COPY_41_DEPTH, mode=Mode.SUBTRACT)

    # 阵列(线性)3 copy 42 sketch → 阵列(线性)3 copy 42 (cut)
    with BuildSketch(Plane(origin=(-202, 5, 582), x_dir=(-1, 0, 0), z_dir=(0, 1, 0))):
        with Locations(Location((-817.5, -589.5, 0), (0, 0, 90))):
            Circle(PATTERN_LINEAR_3_COPY_42_SKETCH_R)
    extrude(amount=-PATTERN_LINEAR_3_COPY_42_DEPTH, mode=Mode.SUBTRACT)

    # 阵列(线性)3 copy 43 sketch → 阵列(线性)3 copy 43 (cut)
    with BuildSketch(Plane(origin=(-303, 5, 582), x_dir=(-1, 0, 0), z_dir=(0, 1, 0))):
        with Locations(Location((-817.5, -589.5, 0), (0, 0, 90))):
            Circle(PATTERN_LINEAR_3_COPY_43_SKETCH_R)
    extrude(amount=-PATTERN_LINEAR_3_COPY_43_DEPTH, mode=Mode.SUBTRACT)

    # 阵列(线性)3 copy 44 sketch → 阵列(线性)3 copy 44 (cut)
    with BuildSketch(Plane(origin=(-404, 5, 582), x_dir=(-1, 0, 0), z_dir=(0, 1, 0))):
        with Locations(Location((-817.5, -589.5, 0), (0, 0, 90))):
            Circle(PATTERN_LINEAR_3_COPY_44_SKETCH_R)
    extrude(amount=-PATTERN_LINEAR_3_COPY_44_DEPTH, mode=Mode.SUBTRACT)

    # 阵列(线性)3 copy 45 sketch → 阵列(线性)3 copy 45 (cut)
    with BuildSketch(Plane(origin=(-505, 5, 582), x_dir=(-1, 0, 0), z_dir=(0, 1, 0))):
        with Locations(Location((-817.5, -589.5, 0), (0, 0, 90))):
            Circle(PATTERN_LINEAR_3_COPY_45_SKETCH_R)
    extrude(amount=-PATTERN_LINEAR_3_COPY_45_DEPTH, mode=Mode.SUBTRACT)

    # 阵列(线性)3 copy 46 sketch → 阵列(线性)3 copy 46 (cut)
    with BuildSketch(Plane(origin=(-606, 5, 582), x_dir=(-1, 0, 0), z_dir=(0, 1, 0))):
        with Locations(Location((-817.5, -589.5, 0), (0, 0, 90))):
            Circle(PATTERN_LINEAR_3_COPY_46_SKETCH_R)
    extrude(amount=-PATTERN_LINEAR_3_COPY_46_DEPTH, mode=Mode.SUBTRACT)

    # 阵列(线性)3 copy 47 sketch → 阵列(线性)3 copy 47 (cut)
    with BuildSketch(Plane(origin=(-707, 5, 582), x_dir=(-1, 0, 0), z_dir=(0, 1, 0))):
        with Locations(Location((-817.5, -589.5, 0), (0, 0, 90))):
            Circle(PATTERN_LINEAR_3_COPY_47_SKETCH_R)
    extrude(amount=-PATTERN_LINEAR_3_COPY_47_DEPTH, mode=Mode.SUBTRACT)

    # 阵列(线性)3 copy 48 sketch → 阵列(线性)3 copy 48 (cut)
    with BuildSketch(Plane(origin=(-808, 5, 582), x_dir=(-1, 0, 0), z_dir=(0, 1, 0))):
        with Locations(Location((-817.5, -589.5, 0), (0, 0, 90))):
            Circle(PATTERN_LINEAR_3_COPY_48_SKETCH_R)
    extrude(amount=-PATTERN_LINEAR_3_COPY_48_DEPTH, mode=Mode.SUBTRACT)

    # 阵列(线性)3 copy 49 sketch → 阵列(线性)3 copy 49 (cut)
    with BuildSketch(Plane(origin=(-101, 5, 0), x_dir=(-1, 0, 0), z_dir=(0, 1, 0))):
        with Locations(Location((-817.5, -589.5, 0), (0, 0, 90))):
            Circle(PATTERN_LINEAR_3_COPY_49_SKETCH_R)
    extrude(amount=-PATTERN_LINEAR_3_COPY_49_DEPTH, mode=Mode.SUBTRACT)

    # 阵列(线性)3 copy 50 sketch → 阵列(线性)3 copy 50 (cut)
    with BuildSketch(Plane(origin=(-202, 5, 0), x_dir=(-1, 0, 0), z_dir=(0, 1, 0))):
        with Locations(Location((-817.5, -589.5, 0), (0, 0, 90))):
            Circle(PATTERN_LINEAR_3_COPY_50_SKETCH_R)
    extrude(amount=-PATTERN_LINEAR_3_COPY_50_DEPTH, mode=Mode.SUBTRACT)

    # 阵列(线性)3 copy 51 sketch → 阵列(线性)3 copy 51 (cut)
    with BuildSketch(Plane(origin=(-303, 5, 0), x_dir=(-1, 0, 0), z_dir=(0, 1, 0))):
        with Locations(Location((-817.5, -589.5, 0), (0, 0, 90))):
            Circle(PATTERN_LINEAR_3_COPY_51_SKETCH_R)
    extrude(amount=-PATTERN_LINEAR_3_COPY_51_DEPTH, mode=Mode.SUBTRACT)

    # 阵列(线性)3 copy 52 sketch → 阵列(线性)3 copy 52 (cut)
    with BuildSketch(Plane(origin=(-404, 5, 0), x_dir=(-1, 0, 0), z_dir=(0, 1, 0))):
        with Locations(Location((-817.5, -589.5, 0), (0, 0, 90))):
            Circle(PATTERN_LINEAR_3_COPY_52_SKETCH_R)
    extrude(amount=-PATTERN_LINEAR_3_COPY_52_DEPTH, mode=Mode.SUBTRACT)

    # 阵列(线性)3 copy 53 sketch → 阵列(线性)3 copy 53 (cut)
    with BuildSketch(Plane(origin=(-505, 5, 0), x_dir=(-1, 0, 0), z_dir=(0, 1, 0))):
        with Locations(Location((-817.5, -589.5, 0), (0, 0, 90))):
            Circle(PATTERN_LINEAR_3_COPY_53_SKETCH_R)
    extrude(amount=-PATTERN_LINEAR_3_COPY_53_DEPTH, mode=Mode.SUBTRACT)

    # 阵列(线性)3 copy 54 sketch → 阵列(线性)3 copy 54 (cut)
    with BuildSketch(Plane(origin=(-606, 5, 0), x_dir=(-1, 0, 0), z_dir=(0, 1, 0))):
        with Locations(Location((-817.5, -589.5, 0), (0, 0, 90))):
            Circle(PATTERN_LINEAR_3_COPY_54_SKETCH_R)
    extrude(amount=-PATTERN_LINEAR_3_COPY_54_DEPTH, mode=Mode.SUBTRACT)

    # 阵列(线性)3 copy 55 sketch → 阵列(线性)3 copy 55 (cut)
    with BuildSketch(Plane(origin=(-707, 5, 0), x_dir=(-1, 0, 0), z_dir=(0, 1, 0))):
        with Locations(Location((-817.5, -589.5, 0), (0, 0, 90))):
            Circle(PATTERN_LINEAR_3_COPY_55_SKETCH_R)
    extrude(amount=-PATTERN_LINEAR_3_COPY_55_DEPTH, mode=Mode.SUBTRACT)

    # 阵列(线性)3 copy 56 sketch → 阵列(线性)3 copy 56 (cut)
    with BuildSketch(Plane(origin=(-808, 5, 0), x_dir=(-1, 0, 0), z_dir=(0, 1, 0))):
        with Locations(Location((-817.5, -589.5, 0), (0, 0, 90))):
            Circle(PATTERN_LINEAR_3_COPY_56_SKETCH_R)
    extrude(amount=-PATTERN_LINEAR_3_COPY_56_DEPTH, mode=Mode.SUBTRACT)


solid = part.part
